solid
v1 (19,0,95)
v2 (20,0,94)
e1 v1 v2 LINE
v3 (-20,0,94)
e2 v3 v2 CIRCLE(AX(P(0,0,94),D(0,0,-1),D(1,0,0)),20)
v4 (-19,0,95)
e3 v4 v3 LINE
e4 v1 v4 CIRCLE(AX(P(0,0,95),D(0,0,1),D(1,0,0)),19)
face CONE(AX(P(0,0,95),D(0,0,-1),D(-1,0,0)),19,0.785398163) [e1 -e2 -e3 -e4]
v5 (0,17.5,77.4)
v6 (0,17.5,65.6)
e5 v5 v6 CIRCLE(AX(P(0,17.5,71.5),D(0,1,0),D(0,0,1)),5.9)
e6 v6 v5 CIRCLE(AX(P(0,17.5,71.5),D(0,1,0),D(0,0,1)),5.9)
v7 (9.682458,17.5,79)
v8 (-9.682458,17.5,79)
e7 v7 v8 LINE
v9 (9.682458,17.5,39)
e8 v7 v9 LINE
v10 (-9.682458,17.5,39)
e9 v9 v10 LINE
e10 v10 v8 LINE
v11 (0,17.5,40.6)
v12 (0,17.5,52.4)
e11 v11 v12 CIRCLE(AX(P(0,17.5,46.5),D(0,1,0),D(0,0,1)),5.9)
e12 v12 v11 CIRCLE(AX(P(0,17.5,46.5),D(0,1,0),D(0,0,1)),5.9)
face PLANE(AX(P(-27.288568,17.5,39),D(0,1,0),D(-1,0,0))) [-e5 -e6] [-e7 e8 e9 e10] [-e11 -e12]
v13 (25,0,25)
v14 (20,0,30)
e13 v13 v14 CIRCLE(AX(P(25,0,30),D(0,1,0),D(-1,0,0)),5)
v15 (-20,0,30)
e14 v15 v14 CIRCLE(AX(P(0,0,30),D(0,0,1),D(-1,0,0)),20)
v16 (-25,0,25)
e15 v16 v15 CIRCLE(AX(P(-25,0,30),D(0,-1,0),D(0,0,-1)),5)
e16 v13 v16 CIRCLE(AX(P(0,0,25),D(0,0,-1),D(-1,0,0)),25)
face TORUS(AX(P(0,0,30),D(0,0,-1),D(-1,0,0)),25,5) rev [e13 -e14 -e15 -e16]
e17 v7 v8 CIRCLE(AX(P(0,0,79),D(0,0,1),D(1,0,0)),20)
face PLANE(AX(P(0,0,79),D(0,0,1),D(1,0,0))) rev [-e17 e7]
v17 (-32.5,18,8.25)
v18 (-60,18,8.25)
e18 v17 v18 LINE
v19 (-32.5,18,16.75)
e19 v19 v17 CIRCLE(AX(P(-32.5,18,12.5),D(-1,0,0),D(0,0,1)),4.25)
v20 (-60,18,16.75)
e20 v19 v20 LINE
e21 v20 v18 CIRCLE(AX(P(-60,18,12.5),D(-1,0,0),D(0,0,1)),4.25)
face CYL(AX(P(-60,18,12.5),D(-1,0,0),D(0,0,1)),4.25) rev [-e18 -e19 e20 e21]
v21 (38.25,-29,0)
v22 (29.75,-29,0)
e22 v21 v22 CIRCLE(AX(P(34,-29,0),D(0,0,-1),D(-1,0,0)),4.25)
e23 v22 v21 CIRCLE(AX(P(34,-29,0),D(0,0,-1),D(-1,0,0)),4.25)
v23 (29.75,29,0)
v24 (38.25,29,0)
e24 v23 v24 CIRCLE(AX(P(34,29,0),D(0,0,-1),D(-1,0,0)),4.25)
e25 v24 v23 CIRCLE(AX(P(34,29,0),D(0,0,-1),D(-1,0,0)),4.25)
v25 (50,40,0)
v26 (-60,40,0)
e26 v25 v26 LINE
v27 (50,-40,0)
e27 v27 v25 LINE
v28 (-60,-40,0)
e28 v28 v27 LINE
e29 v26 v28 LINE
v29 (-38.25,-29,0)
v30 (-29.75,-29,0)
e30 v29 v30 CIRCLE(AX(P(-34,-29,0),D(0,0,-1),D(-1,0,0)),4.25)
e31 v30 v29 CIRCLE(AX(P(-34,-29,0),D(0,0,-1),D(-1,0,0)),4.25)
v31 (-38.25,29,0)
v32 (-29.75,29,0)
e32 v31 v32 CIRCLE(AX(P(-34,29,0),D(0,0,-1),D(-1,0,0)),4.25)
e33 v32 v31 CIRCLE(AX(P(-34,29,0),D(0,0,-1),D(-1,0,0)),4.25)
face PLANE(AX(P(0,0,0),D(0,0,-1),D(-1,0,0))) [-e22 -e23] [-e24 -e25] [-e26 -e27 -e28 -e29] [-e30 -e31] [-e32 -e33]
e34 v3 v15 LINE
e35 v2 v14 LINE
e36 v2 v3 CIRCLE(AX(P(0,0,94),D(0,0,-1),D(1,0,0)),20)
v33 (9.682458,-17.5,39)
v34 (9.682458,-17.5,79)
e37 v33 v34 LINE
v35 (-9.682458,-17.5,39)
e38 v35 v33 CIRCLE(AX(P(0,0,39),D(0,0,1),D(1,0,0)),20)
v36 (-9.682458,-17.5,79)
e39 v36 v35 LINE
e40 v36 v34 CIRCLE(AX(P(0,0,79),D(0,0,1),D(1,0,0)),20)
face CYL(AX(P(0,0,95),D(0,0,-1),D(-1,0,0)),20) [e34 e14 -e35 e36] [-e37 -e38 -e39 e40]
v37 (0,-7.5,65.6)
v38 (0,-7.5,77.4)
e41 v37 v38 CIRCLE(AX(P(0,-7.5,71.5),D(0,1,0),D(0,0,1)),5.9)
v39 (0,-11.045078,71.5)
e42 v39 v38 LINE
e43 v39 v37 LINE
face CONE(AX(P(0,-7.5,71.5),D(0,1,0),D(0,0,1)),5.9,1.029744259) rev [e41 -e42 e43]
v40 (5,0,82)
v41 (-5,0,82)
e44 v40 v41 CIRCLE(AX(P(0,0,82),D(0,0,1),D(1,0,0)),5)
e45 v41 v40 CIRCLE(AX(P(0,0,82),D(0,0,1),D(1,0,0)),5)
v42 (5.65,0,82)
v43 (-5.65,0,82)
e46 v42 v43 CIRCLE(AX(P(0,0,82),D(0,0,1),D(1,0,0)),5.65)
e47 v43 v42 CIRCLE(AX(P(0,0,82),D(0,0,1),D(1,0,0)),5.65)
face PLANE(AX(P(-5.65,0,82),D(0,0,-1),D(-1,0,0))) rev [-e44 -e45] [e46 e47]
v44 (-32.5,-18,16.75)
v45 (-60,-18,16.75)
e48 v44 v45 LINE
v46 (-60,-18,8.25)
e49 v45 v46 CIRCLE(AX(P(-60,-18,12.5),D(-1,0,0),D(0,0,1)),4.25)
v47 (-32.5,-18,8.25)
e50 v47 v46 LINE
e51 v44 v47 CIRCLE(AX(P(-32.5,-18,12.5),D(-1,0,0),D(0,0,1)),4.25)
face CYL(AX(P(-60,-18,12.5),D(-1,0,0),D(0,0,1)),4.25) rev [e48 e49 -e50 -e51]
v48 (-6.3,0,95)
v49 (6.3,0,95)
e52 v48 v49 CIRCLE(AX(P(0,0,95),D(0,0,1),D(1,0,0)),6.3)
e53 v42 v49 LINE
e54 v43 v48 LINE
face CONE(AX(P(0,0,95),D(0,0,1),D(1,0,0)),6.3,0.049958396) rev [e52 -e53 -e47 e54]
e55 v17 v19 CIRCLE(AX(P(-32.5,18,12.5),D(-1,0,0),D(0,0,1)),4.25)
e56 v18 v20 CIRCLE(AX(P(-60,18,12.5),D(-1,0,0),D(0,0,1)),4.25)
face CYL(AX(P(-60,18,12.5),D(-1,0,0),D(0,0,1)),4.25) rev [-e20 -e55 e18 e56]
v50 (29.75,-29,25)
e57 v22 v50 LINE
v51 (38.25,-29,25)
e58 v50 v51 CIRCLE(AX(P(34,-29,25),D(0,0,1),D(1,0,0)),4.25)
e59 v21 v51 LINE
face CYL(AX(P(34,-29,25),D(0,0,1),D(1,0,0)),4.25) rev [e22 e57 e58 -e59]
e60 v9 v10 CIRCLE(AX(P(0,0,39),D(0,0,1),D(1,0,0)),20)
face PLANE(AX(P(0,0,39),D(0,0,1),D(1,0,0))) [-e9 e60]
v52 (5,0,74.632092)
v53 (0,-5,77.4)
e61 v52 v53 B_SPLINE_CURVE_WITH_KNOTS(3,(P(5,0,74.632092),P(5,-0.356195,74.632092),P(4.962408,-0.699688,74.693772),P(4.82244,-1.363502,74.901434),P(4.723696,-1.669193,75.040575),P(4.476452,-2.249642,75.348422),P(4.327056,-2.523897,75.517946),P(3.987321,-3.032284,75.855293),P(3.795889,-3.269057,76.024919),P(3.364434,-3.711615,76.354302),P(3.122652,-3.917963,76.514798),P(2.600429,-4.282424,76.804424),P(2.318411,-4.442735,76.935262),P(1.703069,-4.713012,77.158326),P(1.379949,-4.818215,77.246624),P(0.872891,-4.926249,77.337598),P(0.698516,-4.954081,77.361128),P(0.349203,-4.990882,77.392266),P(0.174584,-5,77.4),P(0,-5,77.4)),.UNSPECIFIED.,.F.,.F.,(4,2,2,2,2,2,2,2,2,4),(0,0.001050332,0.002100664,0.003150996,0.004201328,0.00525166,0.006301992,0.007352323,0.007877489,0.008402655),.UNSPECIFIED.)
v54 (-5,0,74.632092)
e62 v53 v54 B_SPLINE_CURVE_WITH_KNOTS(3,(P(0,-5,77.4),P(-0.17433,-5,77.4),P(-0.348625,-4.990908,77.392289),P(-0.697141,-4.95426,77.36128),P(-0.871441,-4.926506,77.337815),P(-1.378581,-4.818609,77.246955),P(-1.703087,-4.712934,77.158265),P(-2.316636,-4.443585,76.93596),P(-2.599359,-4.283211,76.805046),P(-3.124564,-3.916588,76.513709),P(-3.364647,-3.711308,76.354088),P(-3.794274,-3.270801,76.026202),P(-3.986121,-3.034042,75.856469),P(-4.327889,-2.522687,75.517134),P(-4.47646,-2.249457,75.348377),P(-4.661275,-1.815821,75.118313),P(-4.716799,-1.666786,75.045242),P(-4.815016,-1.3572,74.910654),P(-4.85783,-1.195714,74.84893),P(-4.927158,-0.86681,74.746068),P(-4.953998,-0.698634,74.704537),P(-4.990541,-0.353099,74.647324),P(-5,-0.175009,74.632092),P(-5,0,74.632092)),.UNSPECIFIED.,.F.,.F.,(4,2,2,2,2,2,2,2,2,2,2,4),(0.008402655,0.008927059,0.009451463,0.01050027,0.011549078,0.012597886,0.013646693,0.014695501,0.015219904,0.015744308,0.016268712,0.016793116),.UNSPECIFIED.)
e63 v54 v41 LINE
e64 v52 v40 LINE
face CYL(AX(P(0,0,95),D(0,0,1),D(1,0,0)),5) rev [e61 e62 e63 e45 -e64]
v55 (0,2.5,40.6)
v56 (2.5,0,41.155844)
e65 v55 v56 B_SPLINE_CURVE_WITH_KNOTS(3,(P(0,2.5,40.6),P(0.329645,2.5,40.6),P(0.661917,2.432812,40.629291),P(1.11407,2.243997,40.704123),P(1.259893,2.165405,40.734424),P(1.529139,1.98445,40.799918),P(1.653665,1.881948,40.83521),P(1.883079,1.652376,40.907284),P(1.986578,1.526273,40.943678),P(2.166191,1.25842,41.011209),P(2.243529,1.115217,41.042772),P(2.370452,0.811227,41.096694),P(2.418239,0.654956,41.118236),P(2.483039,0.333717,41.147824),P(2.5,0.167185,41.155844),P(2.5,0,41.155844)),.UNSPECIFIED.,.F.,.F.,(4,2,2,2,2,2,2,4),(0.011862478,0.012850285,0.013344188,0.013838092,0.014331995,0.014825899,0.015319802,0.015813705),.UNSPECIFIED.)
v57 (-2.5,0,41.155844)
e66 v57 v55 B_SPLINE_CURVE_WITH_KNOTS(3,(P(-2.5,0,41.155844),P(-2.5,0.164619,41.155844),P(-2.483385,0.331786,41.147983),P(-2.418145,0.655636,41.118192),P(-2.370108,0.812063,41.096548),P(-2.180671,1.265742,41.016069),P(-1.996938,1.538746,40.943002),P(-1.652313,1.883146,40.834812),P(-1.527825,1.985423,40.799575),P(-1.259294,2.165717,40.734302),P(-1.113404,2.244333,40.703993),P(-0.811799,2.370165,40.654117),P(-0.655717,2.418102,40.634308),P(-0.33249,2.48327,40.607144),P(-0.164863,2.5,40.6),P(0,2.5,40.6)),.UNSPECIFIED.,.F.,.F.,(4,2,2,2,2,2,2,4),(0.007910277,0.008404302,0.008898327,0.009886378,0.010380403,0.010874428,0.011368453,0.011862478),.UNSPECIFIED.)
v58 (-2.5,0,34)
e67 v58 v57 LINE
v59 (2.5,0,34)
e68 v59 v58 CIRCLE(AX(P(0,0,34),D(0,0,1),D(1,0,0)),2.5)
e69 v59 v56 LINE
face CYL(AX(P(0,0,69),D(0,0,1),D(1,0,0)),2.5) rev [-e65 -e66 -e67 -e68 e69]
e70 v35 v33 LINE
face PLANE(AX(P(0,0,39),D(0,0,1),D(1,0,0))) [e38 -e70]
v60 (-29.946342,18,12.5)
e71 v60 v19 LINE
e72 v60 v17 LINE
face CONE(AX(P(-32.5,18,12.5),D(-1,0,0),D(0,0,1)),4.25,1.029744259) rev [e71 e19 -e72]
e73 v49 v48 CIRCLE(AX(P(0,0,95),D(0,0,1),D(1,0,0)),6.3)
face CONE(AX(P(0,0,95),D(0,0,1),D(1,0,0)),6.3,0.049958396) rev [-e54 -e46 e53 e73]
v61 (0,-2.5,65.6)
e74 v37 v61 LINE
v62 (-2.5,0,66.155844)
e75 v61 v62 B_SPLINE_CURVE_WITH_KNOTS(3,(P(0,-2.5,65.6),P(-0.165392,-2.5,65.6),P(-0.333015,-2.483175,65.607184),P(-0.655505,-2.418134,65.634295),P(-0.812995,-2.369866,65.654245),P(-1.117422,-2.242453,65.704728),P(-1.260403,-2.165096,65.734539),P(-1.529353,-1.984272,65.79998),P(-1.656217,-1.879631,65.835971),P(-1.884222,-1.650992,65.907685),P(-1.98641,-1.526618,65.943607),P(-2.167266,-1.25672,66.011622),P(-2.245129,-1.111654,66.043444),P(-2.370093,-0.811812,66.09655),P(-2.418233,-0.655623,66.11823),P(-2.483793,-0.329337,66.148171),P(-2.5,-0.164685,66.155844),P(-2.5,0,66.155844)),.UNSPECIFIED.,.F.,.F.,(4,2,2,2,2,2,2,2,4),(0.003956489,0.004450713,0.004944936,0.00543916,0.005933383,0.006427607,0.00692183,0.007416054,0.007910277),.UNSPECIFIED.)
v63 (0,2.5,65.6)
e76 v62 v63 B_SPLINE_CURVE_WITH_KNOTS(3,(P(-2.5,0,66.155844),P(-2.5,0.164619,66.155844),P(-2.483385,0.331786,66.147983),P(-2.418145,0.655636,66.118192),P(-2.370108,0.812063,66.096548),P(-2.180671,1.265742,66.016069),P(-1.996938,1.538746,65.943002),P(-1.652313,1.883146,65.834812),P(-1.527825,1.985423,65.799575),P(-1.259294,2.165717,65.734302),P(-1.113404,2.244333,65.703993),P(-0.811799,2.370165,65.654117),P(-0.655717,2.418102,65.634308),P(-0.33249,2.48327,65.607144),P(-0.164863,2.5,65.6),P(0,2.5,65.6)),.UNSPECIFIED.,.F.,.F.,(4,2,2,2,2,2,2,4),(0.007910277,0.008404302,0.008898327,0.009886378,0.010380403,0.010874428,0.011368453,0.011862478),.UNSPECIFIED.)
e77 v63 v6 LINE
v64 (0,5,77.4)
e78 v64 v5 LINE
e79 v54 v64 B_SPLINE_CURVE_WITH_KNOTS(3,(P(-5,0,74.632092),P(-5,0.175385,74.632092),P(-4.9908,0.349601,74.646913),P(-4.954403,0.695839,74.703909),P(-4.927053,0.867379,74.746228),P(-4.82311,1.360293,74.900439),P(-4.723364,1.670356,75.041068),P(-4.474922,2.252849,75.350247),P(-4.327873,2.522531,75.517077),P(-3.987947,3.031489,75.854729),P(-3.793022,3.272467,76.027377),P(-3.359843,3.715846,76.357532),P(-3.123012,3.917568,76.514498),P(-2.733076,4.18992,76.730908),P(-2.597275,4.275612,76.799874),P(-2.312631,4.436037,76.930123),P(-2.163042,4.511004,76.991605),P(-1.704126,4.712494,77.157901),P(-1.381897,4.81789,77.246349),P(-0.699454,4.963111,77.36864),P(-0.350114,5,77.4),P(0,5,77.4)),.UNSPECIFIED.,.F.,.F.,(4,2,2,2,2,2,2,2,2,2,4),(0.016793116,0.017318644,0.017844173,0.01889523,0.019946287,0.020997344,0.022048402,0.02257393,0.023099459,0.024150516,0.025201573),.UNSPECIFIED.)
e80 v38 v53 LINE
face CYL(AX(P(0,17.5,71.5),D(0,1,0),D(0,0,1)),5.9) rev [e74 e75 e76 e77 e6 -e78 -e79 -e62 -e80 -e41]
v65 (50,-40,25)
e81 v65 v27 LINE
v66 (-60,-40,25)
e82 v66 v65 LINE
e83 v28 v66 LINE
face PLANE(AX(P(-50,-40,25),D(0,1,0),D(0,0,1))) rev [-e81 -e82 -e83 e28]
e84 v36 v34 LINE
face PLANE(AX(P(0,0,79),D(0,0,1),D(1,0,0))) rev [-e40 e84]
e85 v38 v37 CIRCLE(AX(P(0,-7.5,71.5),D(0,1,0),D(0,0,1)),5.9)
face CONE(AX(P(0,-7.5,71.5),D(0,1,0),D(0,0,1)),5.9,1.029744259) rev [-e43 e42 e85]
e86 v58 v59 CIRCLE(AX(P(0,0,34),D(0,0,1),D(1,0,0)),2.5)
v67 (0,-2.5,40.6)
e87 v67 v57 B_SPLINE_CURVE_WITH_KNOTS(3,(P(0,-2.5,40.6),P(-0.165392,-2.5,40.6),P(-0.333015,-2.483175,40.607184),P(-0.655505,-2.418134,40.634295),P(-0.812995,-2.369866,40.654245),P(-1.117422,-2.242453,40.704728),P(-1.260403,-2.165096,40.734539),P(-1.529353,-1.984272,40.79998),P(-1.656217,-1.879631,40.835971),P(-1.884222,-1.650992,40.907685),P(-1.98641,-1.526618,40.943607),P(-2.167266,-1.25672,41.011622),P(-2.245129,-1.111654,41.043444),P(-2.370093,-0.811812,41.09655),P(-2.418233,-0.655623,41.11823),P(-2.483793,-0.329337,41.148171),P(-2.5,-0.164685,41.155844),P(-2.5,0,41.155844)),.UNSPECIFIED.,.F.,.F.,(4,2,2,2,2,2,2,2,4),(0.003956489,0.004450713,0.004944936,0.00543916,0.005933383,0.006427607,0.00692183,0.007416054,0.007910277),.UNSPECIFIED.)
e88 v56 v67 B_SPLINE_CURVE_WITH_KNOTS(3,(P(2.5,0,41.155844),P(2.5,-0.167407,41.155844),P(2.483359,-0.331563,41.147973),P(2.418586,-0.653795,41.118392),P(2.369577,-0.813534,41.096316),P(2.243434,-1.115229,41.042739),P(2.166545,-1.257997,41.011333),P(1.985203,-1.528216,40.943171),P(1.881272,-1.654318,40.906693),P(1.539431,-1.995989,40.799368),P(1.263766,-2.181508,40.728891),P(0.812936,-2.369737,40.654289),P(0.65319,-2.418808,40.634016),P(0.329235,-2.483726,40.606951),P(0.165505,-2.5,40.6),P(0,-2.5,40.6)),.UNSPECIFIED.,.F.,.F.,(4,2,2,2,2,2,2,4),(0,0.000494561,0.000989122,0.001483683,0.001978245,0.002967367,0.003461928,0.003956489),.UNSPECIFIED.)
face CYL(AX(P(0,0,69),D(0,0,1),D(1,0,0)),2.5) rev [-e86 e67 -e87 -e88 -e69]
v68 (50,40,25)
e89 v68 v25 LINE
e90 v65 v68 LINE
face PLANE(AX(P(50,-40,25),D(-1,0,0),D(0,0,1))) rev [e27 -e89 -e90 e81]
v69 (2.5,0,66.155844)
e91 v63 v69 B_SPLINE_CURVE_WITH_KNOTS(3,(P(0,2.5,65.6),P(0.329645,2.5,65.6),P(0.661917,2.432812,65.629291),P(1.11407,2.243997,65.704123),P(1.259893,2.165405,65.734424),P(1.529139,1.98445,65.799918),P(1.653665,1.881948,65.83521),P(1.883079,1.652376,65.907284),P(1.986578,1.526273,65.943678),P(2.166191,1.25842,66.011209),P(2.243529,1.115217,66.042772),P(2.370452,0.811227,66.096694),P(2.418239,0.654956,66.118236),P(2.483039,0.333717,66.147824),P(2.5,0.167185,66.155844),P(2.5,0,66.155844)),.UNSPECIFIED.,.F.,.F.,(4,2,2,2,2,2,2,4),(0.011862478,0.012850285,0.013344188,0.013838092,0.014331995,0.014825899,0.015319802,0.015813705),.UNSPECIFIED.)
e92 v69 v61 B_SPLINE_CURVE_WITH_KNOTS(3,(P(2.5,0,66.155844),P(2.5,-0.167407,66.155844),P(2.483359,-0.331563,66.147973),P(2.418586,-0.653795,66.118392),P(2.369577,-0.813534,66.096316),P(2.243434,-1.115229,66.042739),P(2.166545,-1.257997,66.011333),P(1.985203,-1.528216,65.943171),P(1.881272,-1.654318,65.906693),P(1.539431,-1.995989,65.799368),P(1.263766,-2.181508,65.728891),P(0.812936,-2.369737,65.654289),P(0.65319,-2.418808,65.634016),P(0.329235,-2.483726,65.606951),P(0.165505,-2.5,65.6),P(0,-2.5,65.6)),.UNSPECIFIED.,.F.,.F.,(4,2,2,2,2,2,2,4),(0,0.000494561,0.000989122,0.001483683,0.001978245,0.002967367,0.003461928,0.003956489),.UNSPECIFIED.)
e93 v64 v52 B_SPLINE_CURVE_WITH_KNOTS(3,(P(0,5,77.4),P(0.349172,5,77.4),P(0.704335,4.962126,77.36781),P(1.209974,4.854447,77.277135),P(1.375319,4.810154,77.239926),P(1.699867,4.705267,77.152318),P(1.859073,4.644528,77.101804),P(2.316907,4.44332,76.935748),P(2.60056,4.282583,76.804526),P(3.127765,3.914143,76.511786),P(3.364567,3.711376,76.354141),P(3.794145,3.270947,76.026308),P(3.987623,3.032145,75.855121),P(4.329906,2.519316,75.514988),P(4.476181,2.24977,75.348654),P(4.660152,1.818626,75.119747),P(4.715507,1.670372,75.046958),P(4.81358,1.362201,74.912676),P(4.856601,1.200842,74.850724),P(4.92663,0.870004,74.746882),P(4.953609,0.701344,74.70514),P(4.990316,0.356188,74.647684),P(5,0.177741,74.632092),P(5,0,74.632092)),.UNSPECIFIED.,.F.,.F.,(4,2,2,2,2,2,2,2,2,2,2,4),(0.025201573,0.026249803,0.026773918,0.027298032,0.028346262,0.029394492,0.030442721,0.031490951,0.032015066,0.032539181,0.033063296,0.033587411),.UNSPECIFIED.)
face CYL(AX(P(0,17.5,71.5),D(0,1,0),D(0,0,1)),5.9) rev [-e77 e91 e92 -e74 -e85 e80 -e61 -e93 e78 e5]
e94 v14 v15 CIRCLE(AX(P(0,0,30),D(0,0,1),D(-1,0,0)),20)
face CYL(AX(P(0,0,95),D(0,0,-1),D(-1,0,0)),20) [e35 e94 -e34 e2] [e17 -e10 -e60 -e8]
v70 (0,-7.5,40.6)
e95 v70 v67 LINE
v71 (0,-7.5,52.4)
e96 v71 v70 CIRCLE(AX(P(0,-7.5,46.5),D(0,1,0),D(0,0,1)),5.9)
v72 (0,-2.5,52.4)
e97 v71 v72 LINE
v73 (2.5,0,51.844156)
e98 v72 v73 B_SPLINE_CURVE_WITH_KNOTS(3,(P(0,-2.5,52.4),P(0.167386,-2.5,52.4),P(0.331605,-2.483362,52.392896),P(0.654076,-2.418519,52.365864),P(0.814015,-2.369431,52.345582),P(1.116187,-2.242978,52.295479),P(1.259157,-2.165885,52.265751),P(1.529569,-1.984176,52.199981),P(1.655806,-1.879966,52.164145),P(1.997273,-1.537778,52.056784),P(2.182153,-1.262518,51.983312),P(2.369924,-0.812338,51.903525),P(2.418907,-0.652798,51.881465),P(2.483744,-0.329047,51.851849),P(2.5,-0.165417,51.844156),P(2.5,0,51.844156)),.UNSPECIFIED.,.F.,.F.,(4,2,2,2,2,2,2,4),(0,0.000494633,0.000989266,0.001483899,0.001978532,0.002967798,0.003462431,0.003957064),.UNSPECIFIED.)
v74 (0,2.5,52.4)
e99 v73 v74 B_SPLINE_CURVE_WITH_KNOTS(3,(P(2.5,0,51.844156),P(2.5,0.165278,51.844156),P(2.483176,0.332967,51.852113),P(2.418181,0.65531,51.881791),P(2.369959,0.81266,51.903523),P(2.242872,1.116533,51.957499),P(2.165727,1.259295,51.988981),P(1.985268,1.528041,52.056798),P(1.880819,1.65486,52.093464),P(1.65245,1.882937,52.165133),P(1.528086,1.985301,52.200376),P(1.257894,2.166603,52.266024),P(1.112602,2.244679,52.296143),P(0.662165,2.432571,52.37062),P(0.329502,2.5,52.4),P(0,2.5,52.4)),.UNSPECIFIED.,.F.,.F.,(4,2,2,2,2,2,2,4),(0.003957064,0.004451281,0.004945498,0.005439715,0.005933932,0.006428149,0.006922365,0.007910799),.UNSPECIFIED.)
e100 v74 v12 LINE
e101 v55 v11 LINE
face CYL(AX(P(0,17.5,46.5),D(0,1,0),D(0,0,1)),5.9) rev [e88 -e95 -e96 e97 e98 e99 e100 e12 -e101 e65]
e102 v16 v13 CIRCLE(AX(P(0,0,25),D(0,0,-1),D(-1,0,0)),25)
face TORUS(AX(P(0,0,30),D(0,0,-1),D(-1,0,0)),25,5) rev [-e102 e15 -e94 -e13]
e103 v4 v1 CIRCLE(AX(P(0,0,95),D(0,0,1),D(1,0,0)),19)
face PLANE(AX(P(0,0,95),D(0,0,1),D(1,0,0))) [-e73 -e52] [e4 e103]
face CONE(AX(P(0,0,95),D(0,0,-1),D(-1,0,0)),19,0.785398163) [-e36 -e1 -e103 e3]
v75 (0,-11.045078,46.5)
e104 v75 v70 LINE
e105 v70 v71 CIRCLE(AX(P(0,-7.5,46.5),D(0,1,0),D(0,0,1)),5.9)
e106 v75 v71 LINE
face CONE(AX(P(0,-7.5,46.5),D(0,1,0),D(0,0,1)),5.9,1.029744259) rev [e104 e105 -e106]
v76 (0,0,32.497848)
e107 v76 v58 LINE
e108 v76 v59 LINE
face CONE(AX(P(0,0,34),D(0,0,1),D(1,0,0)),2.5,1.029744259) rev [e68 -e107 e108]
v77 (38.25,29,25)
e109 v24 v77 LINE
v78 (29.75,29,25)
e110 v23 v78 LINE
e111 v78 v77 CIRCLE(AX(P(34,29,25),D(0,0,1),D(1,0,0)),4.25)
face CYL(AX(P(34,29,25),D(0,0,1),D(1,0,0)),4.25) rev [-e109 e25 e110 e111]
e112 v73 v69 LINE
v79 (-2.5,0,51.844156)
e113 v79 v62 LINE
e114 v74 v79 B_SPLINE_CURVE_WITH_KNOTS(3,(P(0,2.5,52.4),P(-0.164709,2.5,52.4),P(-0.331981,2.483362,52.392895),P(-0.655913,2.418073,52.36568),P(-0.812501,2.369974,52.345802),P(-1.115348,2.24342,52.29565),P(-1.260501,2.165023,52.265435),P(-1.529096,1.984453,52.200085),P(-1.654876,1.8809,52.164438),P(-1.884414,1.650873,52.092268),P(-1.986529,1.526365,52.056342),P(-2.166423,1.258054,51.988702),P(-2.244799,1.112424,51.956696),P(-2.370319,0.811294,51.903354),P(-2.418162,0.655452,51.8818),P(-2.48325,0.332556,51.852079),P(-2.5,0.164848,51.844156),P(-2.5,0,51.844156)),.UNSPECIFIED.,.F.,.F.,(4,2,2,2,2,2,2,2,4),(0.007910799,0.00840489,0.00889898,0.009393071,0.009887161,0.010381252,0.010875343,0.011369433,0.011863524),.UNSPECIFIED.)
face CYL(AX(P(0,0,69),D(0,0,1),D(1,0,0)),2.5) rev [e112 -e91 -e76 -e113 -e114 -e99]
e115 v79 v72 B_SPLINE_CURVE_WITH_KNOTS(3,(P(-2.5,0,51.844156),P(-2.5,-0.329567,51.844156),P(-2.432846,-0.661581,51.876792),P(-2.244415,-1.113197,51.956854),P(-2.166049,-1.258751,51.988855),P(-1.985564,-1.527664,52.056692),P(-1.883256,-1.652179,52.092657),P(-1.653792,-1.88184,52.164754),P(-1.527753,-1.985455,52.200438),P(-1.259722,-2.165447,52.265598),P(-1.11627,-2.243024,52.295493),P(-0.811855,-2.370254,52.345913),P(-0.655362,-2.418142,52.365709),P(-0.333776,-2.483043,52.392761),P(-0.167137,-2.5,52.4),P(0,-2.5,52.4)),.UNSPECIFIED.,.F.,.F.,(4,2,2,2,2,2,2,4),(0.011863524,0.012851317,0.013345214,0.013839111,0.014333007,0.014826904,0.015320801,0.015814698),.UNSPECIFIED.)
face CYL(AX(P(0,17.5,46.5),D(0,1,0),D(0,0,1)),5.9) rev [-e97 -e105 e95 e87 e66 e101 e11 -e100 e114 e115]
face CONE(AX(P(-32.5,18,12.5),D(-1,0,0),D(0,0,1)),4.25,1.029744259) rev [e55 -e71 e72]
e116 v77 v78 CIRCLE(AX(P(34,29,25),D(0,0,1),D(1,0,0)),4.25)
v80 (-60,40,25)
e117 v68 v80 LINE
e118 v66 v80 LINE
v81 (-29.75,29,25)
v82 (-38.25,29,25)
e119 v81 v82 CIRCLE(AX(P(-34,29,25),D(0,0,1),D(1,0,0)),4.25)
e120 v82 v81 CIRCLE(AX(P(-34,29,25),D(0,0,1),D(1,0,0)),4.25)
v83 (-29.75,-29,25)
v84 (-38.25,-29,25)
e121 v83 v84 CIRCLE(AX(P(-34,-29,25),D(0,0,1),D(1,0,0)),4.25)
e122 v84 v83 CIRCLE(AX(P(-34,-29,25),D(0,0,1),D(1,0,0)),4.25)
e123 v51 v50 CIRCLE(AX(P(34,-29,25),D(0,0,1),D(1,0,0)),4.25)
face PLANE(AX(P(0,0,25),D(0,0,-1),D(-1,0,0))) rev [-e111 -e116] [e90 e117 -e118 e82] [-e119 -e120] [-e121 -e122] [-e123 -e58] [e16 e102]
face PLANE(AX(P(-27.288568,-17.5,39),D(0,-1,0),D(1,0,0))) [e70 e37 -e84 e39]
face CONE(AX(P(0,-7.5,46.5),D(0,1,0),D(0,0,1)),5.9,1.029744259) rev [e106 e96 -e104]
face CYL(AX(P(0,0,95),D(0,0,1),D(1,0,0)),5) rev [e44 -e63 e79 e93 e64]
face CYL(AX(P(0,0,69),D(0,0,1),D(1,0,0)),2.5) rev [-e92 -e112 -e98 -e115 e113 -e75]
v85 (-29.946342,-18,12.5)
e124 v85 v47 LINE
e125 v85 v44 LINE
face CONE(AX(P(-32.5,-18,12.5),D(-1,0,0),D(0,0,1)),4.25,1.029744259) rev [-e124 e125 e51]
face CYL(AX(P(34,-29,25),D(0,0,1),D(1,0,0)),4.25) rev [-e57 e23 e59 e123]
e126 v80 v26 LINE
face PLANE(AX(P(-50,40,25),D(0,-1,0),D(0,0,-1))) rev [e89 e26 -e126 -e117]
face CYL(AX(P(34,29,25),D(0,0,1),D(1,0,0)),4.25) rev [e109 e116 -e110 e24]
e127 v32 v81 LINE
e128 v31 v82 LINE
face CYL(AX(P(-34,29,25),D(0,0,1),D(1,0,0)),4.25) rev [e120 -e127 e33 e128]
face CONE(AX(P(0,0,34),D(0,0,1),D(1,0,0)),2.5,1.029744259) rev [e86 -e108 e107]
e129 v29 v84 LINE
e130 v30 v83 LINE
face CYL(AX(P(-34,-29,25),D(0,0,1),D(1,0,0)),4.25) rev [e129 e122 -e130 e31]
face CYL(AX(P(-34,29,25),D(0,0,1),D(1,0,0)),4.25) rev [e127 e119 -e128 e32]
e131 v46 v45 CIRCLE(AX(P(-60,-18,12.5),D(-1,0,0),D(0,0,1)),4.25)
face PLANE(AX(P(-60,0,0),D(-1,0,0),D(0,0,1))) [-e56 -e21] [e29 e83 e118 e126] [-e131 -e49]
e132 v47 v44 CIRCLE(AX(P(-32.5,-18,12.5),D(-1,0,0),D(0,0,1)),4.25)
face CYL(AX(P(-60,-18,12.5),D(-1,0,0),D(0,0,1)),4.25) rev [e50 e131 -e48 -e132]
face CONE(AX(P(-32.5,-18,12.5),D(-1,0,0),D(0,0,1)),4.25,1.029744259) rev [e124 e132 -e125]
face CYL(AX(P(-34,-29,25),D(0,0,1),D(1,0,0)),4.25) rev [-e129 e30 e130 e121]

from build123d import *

# Parameters (mm, degrees)
SKETCH_13_W                 = 100
SKETCH_13_H                 = 80
EXTRUDE_3_DEPTH             = 25
SKETCH_14_R                 = 0.5
CUT_EXTRUDE_4_DEPTH         = 18
SKETCH_15_R                 = 20
EXTRUDE_4_DEPTH             = 70
HOLE_WIZARD_10_0_10_1_D     = 10
HOLE_WIZARD_10_0_10_1_DEPTH = 25
HOLE_WIZARD_10_0_10_1_TIP   = 3.004303095
SKETCH_21_OUTSIDE_W         = 133.89
SKETCH_21_OUTSIDE_H         = 113.89
SKETCH_21_OUTSIDE_W_2       = 54.577135948
SKETCH_21_OUTSIDE_H_2       = 35
CUT_EXTRUDE_5_DEPTH         = 40
HOLE_WIZARD_G1_4_1_D        = 11.8
HOLE_WIZARD_G1_4_1_DEPTH    = 25
HOLE_WIZARD_G1_4_1_TIP      = 3.545077652
CHAMFER_1_SIZE              = 1
HOLE_WIZARD_M10_1_D         = 8.5
HOLE_WIZARD_M10_1_DEPTH     = 27.5
HOLE_WIZARD_M10_1_TIP       = 2.553657631
FILLET_1_R                  = 5
HOLE_WIZARD_M6_1_D          = 5
HOLE_WIZARD_M6_1_DEPTH      = 35
HOLE_WIZARD_M6_1_TIP        = 1.502151548
SKETCH_29_W                 = 25
SKETCH_29_H                 = 80
EXTRUDE_5_DEPTH             = 10
HOLE_WIZARD_M10_2_D         = 8.5
HOLE_WIZARD_M10_2_DEPTH     = 27.5
HOLE_WIZARD_M10_2_TIP       = 2.553657631


with BuildPart() as part:
    # 草图13 → 凸台-拉伸3 (new body)
    with BuildSketch(Plane.XY):
        Rectangle(SKETCH_13_W, SKETCH_13_H)
    extrude(amount=EXTRUDE_3_DEPTH)

    # 草图14 → 切除-拉伸4 (cut)
    with BuildSketch(Plane.XY.offset(25)):
        with Locations((-34, 29)):
            Circle(SKETCH_14_R)
        with Locations((34, 29)):
            Circle(SKETCH_14_R)
        with Locations((34, -29)):
            Circle(SKETCH_14_R)
        with Locations((-34, -29)):
            Circle(SKETCH_14_R)
    extrude(amount=-CUT_EXTRUDE_4_DEPTH, mode=Mode.SUBTRACT)

    # 草图15 → 凸台-拉伸4 (add)
    with BuildSketch(Plane.XY.offset(25)):
        with Locations(Location((0, 0, 0), (0, 0, 180))):
            Circle(SKETCH_15_R)
    extrude(amount=EXTRUDE_4_DEPTH)

    # Ø10.0 (10) 直径孔1
    with Locations(Plane.XY.offset(95)):
        with Locations((0, 0)):
            Hole(HOLE_WIZARD_10_0_10_1_D / 2, depth=HOLE_WIZARD_10_0_10_1_DEPTH)
            with Locations((0, 0, -(HOLE_WIZARD_10_0_10_1_DEPTH + HOLE_WIZARD_10_0_10_1_TIP / 2))):  # 118° drill point
                Cone(0, HOLE_WIZARD_10_0_10_1_D / 2, HOLE_WIZARD_10_0_10_1_TIP, mode=Mode.SUBTRACT)

    # 草图19 → 切除-旋转10 (revolve, cut)
    with BuildSketch(Plane(origin=(0, 0, 0), x_dir=(1, 0, 0), z_dir=(0, 1, 0)), mode=Mode.PRIVATE) as cut_revolve_10_sk:
        Polygon((-6.3, -95), (-5.65, -82), (-5, -82), (-5, -95), align=None)
    revolve(cut_revolve_10_sk.sketch.rotate(Axis((0, 0, 95), (0, 0, -1)), 180), axis=Axis((0, 0, 95), (0, 0, -1)), mode=Mode.SUBTRACT)

    # 草图21 outside → 切除-拉伸5 (cut)
    with BuildSketch(Plane.XY.offset(79)):
        Rectangle(SKETCH_21_OUTSIDE_W, SKETCH_21_OUTSIDE_H)
        Rectangle(SKETCH_21_OUTSIDE_W_2, SKETCH_21_OUTSIDE_H_2, mode=Mode.SUBTRACT)
    extrude(amount=-CUT_EXTRUDE_5_DEPTH, mode=Mode.SUBTRACT)

    # G1/4 螺纹孔1
    with Locations(Plane(origin=(0, 17.5, 0), x_dir=(1, 0, 0), z_dir=(0, 1, 0))):
        with Locations((0, -71.5), (0, -46.5)):
            Hole(HOLE_WIZARD_G1_4_1_D / 2, depth=HOLE_WIZARD_G1_4_1_DEPTH)
            with Locations((0, 0, -(HOLE_WIZARD_G1_4_1_DEPTH + HOLE_WIZARD_G1_4_1_TIP / 2))):  # 118° drill point
                Cone(0, HOLE_WIZARD_G1_4_1_D / 2, HOLE_WIZARD_G1_4_1_TIP, mode=Mode.SUBTRACT)

    # 倒角1
    chamfer_1_edges = [part.edges().sort_by_distance(p)[0] for p in [
        (20, 0, 95),
    ]]
    chamfer(chamfer_1_edges, length=CHAMFER_1_SIZE)

    # M10 螺纹孔1
    with Locations(Plane.XY.offset(25)):
        with Locations((-34, 29), (34, 29), (34, -29), (-34, -29)):
            Hole(HOLE_WIZARD_M10_1_D / 2, depth=HOLE_WIZARD_M10_1_DEPTH)
            with Locations((0, 0, -(HOLE_WIZARD_M10_1_DEPTH + HOLE_WIZARD_M10_1_TIP / 2))):  # 118° drill point
                Cone(0, HOLE_WIZARD_M10_1_D / 2, HOLE_WIZARD_M10_1_TIP, mode=Mode.SUBTRACT)

    # 圆角1
    fillet_1_edges = [part.edges().sort_by_distance(p)[0] for p in [
        (20, 0, 25),
    ]]
    fillet(fillet_1_edges, radius=FILLET_1_R)

    # M6 螺纹孔1
    with Locations(Plane.XY.offset(69)):
        with Locations((0, 0)):
            Hole(HOLE_WIZARD_M6_1_D / 2, depth=HOLE_WIZARD_M6_1_DEPTH)
            with Locations((0, 0, -(HOLE_WIZARD_M6_1_DEPTH + HOLE_WIZARD_M6_1_TIP / 2))):  # 118° drill point
                Cone(0, HOLE_WIZARD_M6_1_D / 2, HOLE_WIZARD_M6_1_TIP, mode=Mode.SUBTRACT)

    # 草图29 → 凸台-拉伸5 (add)
    with BuildSketch(Plane.ZY.offset(50)):
        with Locations((12.5, 0)):
            Rectangle(SKETCH_29_W, SKETCH_29_H)
    extrude(amount=EXTRUDE_5_DEPTH)

    # M10 螺纹孔2
    with Locations(Plane.ZY.offset(60)):
        with Locations((12.5, -18), (12.5, 18)):
            Hole(HOLE_WIZARD_M10_2_D / 2, depth=HOLE_WIZARD_M10_2_DEPTH)
            with Locations((0, 0, -(HOLE_WIZARD_M10_2_DEPTH + HOLE_WIZARD_M10_2_TIP / 2))):  # 118° drill point
                Cone(0, HOLE_WIZARD_M10_2_D / 2, HOLE_WIZARD_M10_2_TIP, mode=Mode.SUBTRACT)


solid = part.part
